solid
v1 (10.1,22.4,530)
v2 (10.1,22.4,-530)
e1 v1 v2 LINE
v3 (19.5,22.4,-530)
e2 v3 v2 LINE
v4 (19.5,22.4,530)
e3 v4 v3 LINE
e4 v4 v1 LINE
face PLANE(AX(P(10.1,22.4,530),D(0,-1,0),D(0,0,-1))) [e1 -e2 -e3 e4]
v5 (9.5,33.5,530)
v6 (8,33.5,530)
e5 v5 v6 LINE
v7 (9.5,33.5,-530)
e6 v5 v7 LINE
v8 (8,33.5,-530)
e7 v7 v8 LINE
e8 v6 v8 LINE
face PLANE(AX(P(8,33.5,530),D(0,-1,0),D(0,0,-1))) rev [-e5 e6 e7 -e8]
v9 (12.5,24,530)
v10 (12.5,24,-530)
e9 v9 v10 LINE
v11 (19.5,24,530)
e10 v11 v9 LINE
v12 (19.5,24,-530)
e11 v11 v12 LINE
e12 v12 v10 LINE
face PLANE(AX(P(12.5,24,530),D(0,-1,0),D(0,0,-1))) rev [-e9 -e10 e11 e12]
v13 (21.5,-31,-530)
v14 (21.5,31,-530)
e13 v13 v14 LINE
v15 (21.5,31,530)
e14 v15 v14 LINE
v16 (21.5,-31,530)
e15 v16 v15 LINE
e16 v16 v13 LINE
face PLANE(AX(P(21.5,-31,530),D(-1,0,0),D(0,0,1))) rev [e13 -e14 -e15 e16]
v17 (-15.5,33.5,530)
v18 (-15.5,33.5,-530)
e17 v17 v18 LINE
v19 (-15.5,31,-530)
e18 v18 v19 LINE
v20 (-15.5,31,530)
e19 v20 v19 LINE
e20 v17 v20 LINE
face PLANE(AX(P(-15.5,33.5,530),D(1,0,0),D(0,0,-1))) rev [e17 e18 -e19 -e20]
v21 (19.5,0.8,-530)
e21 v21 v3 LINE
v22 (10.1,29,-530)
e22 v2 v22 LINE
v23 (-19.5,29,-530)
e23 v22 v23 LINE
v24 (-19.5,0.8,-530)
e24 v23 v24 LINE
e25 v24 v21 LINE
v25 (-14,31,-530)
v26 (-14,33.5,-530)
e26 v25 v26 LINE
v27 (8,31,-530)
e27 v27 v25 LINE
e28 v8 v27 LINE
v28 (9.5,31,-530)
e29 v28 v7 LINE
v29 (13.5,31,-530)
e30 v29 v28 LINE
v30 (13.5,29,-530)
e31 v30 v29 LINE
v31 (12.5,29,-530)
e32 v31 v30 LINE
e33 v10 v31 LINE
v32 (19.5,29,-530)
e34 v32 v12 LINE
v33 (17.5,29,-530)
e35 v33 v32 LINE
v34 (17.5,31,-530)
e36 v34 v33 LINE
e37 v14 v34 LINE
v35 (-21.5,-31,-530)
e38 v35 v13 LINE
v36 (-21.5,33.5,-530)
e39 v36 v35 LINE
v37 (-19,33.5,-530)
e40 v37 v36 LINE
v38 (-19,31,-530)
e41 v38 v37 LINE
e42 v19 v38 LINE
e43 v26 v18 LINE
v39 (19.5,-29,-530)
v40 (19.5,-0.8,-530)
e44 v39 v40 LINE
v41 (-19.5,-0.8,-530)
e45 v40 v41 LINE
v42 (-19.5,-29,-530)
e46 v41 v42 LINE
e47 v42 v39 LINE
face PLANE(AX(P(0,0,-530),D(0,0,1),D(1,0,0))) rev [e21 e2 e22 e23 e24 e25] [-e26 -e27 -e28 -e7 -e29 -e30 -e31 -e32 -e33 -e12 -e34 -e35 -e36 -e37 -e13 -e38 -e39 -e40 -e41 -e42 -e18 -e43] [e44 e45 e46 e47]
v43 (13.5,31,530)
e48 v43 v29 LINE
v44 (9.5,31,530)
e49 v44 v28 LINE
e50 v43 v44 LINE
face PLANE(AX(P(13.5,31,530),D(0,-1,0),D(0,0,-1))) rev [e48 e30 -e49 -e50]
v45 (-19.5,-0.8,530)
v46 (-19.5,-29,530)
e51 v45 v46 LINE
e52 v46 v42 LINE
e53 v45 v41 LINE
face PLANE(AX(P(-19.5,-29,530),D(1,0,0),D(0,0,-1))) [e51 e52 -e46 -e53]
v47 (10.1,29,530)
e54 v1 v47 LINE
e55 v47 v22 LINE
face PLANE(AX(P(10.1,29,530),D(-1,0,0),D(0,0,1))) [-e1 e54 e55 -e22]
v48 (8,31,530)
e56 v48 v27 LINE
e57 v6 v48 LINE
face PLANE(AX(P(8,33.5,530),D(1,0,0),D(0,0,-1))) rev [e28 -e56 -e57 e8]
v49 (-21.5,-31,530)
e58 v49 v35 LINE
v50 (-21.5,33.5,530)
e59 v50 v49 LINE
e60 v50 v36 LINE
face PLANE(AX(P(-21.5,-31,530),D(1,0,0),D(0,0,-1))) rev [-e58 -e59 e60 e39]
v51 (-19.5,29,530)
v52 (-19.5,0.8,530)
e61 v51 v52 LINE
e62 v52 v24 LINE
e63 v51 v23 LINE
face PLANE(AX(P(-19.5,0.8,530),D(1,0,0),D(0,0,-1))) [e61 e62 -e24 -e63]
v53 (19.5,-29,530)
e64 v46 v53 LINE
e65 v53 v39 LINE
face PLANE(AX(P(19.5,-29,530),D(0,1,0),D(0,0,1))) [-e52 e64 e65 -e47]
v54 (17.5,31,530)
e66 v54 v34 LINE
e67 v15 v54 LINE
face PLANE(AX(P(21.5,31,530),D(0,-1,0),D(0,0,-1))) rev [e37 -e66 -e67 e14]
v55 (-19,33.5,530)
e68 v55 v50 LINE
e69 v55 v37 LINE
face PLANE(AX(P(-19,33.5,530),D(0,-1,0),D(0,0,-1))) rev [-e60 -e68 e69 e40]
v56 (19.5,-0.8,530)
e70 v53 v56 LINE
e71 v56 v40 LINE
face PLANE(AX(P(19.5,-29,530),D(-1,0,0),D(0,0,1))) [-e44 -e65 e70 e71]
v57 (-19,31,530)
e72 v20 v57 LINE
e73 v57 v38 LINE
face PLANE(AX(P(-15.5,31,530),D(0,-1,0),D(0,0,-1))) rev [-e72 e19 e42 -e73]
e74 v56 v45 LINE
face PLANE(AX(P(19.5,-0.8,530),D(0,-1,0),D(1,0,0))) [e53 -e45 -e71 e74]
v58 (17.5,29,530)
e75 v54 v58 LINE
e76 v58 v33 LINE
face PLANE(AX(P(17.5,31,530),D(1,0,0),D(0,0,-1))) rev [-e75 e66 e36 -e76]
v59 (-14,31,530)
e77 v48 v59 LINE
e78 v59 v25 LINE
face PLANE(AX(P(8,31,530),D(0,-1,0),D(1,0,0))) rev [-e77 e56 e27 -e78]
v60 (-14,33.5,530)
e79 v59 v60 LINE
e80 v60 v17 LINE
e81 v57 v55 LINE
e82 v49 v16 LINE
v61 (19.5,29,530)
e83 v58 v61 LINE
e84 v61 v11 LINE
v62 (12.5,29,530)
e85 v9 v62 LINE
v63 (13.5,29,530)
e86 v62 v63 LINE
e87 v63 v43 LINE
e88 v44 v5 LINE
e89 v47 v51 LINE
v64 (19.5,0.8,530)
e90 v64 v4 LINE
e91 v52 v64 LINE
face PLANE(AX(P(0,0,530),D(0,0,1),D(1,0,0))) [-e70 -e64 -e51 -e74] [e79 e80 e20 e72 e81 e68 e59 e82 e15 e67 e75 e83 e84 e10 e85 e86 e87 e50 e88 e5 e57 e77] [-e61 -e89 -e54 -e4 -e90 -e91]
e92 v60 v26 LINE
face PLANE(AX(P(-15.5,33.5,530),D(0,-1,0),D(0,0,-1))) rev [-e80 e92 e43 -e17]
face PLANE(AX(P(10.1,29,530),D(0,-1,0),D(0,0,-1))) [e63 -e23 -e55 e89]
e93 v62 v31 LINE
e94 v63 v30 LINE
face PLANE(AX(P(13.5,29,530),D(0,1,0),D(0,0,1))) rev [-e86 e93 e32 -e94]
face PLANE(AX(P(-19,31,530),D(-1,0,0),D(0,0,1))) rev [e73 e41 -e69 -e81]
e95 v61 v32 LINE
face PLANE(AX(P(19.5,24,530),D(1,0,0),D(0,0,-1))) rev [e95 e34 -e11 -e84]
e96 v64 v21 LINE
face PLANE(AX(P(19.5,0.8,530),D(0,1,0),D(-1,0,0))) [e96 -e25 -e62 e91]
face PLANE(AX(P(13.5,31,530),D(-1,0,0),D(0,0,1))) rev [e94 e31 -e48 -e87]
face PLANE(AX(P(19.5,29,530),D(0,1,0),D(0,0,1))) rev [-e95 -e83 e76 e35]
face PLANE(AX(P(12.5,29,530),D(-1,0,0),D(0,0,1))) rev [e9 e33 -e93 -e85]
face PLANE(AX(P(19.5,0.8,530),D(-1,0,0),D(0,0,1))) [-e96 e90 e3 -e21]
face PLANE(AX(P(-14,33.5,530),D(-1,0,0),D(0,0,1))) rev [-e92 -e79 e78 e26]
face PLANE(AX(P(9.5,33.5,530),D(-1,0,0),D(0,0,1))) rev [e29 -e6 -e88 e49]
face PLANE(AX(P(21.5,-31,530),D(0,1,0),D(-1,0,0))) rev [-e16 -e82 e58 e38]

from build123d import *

# Parameters (mm, degrees)
SKETCH1_W           = 39
SKETCH1_H           = 28.2
BOSS_EXTRUDE1_DEPTH = 530


with BuildPart() as part:
    # Sketch1 → Boss-Extrude1 (new, symmetric)
    with BuildSketch(Plane.XY):
        Polygon((21.5, -31), (-21.5, -31), (-21.5, 31), (-21.5, 33.5), (-19, 33.5), (-19, 31), (-15.5, 31), (-15.5, 33.5), (-14, 33.5), (-14, 31), (8, 31), (8, 33.5), (9.5, 33.5), (9.5, 31), (13.5, 31), (13.5, 29), (12.5, 29), (12.5, 24), (19.5, 24), (19.5, 29), (17.5, 29), (17.5, 31), (21.5, 31), align=None)
        Polygon((19.5, 0.8), (-19.5, 0.8), (-19.5, 29), (10.1, 29), (10.1, 22.4), (19.5, 22.4), align=None, mode=Mode.SUBTRACT)
        with Locations((0, -14.9)):
            Rectangle(SKETCH1_W, SKETCH1_H, mode=Mode.SUBTRACT)
    extrude(amount=BOSS_EXTRUDE1_DEPTH, both=True)


solid = part.part
